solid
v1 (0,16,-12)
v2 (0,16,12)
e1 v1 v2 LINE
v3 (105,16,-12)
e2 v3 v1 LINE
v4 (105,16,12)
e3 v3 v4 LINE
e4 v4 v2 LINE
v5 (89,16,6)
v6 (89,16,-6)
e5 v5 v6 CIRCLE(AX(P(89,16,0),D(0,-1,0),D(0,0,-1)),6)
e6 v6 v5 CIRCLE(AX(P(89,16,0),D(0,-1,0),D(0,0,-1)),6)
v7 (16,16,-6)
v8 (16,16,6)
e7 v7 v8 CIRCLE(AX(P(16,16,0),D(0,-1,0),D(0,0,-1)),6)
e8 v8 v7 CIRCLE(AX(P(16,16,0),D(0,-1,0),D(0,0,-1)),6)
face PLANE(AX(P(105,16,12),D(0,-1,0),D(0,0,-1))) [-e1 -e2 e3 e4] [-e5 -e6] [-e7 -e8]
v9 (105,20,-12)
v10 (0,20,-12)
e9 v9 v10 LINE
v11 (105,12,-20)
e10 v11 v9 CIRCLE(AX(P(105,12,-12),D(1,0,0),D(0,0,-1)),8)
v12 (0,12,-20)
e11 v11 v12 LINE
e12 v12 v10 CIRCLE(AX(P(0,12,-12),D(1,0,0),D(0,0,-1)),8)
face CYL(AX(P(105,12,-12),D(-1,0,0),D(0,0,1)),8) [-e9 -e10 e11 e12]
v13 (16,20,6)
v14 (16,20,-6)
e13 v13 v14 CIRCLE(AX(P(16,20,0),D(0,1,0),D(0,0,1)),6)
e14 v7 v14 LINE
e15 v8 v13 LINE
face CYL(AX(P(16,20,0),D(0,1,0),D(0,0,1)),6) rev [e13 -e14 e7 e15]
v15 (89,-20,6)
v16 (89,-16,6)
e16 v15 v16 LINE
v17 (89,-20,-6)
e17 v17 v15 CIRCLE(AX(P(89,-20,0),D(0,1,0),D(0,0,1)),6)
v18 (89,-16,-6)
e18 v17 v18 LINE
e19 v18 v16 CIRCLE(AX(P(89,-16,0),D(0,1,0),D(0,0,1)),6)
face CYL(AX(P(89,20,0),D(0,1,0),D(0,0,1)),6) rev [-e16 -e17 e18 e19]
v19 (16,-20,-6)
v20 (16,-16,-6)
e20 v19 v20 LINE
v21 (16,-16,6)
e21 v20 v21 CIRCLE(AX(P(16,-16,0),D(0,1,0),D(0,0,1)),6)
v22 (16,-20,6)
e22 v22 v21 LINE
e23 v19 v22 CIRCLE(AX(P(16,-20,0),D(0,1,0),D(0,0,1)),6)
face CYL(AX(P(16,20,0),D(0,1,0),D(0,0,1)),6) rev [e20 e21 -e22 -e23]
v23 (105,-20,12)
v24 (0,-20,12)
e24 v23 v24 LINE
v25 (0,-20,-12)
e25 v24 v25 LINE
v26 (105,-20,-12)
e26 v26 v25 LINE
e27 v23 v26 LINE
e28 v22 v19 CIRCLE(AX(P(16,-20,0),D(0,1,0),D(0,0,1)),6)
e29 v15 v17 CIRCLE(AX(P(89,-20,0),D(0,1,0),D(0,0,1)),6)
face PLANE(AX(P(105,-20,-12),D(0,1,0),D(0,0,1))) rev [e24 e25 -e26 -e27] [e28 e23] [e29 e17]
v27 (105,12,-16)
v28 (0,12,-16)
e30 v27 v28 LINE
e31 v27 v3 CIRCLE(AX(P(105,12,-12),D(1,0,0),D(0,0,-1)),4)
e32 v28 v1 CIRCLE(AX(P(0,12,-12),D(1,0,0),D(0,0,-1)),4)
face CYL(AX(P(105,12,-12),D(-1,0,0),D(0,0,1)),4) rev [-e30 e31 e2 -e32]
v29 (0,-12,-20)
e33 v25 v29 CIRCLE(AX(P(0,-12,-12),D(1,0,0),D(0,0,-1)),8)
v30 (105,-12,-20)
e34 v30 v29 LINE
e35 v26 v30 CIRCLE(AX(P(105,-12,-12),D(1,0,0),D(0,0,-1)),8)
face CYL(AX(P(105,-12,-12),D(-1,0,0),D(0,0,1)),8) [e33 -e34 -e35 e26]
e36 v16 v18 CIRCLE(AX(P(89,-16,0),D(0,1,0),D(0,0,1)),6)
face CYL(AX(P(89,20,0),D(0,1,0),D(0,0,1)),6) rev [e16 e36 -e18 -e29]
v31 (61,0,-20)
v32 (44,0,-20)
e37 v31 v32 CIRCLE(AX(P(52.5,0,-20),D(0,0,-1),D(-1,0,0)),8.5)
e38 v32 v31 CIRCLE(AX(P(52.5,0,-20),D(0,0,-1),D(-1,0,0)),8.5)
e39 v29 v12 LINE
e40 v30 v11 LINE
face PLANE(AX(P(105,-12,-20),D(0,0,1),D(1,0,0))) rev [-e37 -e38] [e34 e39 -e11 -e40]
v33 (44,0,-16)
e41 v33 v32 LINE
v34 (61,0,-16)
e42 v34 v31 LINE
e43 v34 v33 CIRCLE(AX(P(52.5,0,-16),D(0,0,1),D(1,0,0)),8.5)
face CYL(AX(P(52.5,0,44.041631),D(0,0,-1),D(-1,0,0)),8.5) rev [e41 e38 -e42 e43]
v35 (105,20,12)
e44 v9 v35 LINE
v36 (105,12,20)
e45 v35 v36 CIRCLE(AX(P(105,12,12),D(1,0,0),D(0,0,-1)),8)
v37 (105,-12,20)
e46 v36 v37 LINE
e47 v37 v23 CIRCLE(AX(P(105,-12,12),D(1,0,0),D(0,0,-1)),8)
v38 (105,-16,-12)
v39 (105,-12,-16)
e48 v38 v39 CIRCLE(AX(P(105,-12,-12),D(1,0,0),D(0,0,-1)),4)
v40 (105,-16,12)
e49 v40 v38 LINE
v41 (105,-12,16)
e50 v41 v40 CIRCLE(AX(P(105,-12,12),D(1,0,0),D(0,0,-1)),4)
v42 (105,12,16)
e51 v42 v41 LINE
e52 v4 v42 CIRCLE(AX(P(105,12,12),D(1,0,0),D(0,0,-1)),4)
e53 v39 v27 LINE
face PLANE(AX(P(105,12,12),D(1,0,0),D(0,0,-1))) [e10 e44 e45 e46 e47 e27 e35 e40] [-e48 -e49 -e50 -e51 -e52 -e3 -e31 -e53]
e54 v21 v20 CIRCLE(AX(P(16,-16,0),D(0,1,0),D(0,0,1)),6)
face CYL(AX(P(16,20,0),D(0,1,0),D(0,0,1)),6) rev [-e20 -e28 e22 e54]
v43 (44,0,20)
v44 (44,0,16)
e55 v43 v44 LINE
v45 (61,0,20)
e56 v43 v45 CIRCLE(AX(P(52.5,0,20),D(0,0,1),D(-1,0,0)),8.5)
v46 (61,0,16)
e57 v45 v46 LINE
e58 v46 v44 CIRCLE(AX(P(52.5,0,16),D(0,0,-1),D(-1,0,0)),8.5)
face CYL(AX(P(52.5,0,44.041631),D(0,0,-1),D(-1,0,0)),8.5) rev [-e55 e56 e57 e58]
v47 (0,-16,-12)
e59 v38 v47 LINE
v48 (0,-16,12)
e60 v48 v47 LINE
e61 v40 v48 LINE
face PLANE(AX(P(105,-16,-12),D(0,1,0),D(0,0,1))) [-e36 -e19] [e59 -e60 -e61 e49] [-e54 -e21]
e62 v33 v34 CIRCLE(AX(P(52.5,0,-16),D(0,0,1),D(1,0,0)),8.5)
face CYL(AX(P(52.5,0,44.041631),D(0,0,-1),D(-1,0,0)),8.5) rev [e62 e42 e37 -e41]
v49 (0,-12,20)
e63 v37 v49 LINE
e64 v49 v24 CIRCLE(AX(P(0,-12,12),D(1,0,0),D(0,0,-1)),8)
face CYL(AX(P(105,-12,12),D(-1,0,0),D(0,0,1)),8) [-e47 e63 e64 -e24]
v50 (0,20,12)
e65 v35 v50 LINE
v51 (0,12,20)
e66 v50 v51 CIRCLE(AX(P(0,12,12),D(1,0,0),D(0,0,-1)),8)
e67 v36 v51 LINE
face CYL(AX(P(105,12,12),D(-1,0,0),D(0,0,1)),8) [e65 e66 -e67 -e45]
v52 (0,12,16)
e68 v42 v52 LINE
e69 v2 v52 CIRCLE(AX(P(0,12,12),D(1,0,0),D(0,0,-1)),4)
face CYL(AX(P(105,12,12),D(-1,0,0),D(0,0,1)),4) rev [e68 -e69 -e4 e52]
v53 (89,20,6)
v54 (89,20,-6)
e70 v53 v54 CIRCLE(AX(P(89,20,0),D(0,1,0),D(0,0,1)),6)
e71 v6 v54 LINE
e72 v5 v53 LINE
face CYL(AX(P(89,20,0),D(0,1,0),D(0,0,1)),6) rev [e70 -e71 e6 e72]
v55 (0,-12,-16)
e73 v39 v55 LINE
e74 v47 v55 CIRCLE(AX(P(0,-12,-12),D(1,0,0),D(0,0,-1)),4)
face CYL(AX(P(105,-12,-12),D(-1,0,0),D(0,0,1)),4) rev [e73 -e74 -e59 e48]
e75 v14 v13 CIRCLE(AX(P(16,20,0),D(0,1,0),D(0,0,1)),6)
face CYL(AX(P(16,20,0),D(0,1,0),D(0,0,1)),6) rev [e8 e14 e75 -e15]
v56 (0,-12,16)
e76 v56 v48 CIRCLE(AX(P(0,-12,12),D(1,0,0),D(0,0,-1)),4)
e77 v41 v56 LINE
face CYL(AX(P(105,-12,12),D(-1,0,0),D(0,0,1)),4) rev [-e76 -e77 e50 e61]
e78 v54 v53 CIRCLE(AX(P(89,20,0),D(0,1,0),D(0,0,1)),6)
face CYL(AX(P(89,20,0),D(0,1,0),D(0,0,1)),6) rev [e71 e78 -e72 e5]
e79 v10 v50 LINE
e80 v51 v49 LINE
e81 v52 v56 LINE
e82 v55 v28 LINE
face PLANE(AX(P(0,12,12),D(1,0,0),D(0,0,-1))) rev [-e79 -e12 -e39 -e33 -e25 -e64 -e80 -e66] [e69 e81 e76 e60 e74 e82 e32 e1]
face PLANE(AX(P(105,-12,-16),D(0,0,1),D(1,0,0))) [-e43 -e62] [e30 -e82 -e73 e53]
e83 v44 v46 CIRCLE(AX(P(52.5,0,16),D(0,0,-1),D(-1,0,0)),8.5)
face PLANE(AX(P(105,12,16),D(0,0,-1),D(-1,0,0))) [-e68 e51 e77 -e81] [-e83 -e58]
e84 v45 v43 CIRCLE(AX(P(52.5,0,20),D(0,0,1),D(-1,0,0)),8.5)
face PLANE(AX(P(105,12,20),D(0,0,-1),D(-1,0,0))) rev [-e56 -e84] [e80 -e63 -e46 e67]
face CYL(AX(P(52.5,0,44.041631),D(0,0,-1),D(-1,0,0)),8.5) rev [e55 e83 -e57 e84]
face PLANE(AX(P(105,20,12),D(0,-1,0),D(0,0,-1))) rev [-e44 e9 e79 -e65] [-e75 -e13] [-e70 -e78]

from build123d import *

# Parameters (mm, degrees)
GB_T6728_2002_40_X_40_X_4_1_DEPTH = 105
HOLE_WIZARD_12_0_12_1_D           = 12
HOLE_WIZARD_12_0_12_1_DEPTH       = 41.394836286
HOLE_WIZARD_12_0_12_1_TIP         = 3.605163714
CUT_EXTRUDE_1_REACH               = 116.127
SKETCH_5_R                        = 8.5


with BuildPart() as part:
    # Sketch1 → 冷弯空心方管gb∕t6728-2002 40 X 40 X 4(1) (new body)
    with BuildSketch(Plane.YZ):
        with BuildLine():
            Line((-12, -20), (12, -20))
            ThreePointArc((12, -20), (17.656854249, -17.656854249), (20, -12))
            Line((20, -12), (20, 12))
            ThreePointArc((20, 12), (17.656854249, 17.656854249), (12, 20))
            Line((12, 20), (-12, 20))
            ThreePointArc((-12, 20), (-17.656854249, 17.656854249), (-20, 12))
            Line((-20, 12), (-20, -12))
            ThreePointArc((-20, -12), (-17.656854249, -17.656854249), (-12, -20))
        make_face()
        with BuildLine():
            Line((-12, -16), (12, -16))
            ThreePointArc((12, -16), (14.828427125, -14.828427125), (16, -12))
            Line((16, -12), (16, 12))
            ThreePointArc((16, 12), (14.828427125, 14.828427125), (12, 16))
            Line((12, 16), (-12, 16))
            ThreePointArc((-12, 16), (-14.828427125, 14.828427125), (-16, 12))
            Line((-16, 12), (-16, -12))
            ThreePointArc((-16, -12), (-14.828427125, -14.828427125), (-12, -16))
        make_face(mode=Mode.SUBTRACT)
    extrude(amount=GB_T6728_2002_40_X_40_X_4_1_DEPTH)

    # Ø12.0 (12) 直径孔1
    with Locations(Plane(origin=(0, 20, 0), x_dir=(1, 0, 0), z_dir=(0, 1, 0))):
        with Locations((16, 0), (89, 0)):
            Hole(HOLE_WIZARD_12_0_12_1_D / 2, depth=HOLE_WIZARD_12_0_12_1_DEPTH)
            with Locations((0, 0, -(HOLE_WIZARD_12_0_12_1_DEPTH + HOLE_WIZARD_12_0_12_1_TIP / 2))):  # 118° drill point
                Cone(0, HOLE_WIZARD_12_0_12_1_D / 2, HOLE_WIZARD_12_0_12_1_TIP, mode=Mode.SUBTRACT)

    # 切除-拉伸1: up to this face of the body (flat: up to its plane)
    cut_extrude_1_end = Plane(part.part.faces().sort_by_distance((52.5, 0, 20))[0])
    # 草图5 → 切除-拉伸1 (cut, up to the picked face)
    with BuildSketch(Plane(origin=(0, 0, -20), x_dir=(-1, 0, 0), z_dir=(0, 0, -1)), mode=Mode.PRIVATE) as cut_extrude_1_sk1:
        with Locations((-52.5, 0)):
            Circle(SKETCH_5_R)
    cut_extrude_1_tool1 = split(extrude(cut_extrude_1_sk1.sketch, amount=-CUT_EXTRUDE_1_REACH, mode=Mode.PRIVATE), bisect_by=cut_extrude_1_end, keep=Keep.BOTH, mode=Mode.PRIVATE)
    add(cut_extrude_1_tool1.solids().sort_by(Axis((52.5, 0, -20), (0, 0, 1)))[0], mode=Mode.SUBTRACT)


solid = part.part
